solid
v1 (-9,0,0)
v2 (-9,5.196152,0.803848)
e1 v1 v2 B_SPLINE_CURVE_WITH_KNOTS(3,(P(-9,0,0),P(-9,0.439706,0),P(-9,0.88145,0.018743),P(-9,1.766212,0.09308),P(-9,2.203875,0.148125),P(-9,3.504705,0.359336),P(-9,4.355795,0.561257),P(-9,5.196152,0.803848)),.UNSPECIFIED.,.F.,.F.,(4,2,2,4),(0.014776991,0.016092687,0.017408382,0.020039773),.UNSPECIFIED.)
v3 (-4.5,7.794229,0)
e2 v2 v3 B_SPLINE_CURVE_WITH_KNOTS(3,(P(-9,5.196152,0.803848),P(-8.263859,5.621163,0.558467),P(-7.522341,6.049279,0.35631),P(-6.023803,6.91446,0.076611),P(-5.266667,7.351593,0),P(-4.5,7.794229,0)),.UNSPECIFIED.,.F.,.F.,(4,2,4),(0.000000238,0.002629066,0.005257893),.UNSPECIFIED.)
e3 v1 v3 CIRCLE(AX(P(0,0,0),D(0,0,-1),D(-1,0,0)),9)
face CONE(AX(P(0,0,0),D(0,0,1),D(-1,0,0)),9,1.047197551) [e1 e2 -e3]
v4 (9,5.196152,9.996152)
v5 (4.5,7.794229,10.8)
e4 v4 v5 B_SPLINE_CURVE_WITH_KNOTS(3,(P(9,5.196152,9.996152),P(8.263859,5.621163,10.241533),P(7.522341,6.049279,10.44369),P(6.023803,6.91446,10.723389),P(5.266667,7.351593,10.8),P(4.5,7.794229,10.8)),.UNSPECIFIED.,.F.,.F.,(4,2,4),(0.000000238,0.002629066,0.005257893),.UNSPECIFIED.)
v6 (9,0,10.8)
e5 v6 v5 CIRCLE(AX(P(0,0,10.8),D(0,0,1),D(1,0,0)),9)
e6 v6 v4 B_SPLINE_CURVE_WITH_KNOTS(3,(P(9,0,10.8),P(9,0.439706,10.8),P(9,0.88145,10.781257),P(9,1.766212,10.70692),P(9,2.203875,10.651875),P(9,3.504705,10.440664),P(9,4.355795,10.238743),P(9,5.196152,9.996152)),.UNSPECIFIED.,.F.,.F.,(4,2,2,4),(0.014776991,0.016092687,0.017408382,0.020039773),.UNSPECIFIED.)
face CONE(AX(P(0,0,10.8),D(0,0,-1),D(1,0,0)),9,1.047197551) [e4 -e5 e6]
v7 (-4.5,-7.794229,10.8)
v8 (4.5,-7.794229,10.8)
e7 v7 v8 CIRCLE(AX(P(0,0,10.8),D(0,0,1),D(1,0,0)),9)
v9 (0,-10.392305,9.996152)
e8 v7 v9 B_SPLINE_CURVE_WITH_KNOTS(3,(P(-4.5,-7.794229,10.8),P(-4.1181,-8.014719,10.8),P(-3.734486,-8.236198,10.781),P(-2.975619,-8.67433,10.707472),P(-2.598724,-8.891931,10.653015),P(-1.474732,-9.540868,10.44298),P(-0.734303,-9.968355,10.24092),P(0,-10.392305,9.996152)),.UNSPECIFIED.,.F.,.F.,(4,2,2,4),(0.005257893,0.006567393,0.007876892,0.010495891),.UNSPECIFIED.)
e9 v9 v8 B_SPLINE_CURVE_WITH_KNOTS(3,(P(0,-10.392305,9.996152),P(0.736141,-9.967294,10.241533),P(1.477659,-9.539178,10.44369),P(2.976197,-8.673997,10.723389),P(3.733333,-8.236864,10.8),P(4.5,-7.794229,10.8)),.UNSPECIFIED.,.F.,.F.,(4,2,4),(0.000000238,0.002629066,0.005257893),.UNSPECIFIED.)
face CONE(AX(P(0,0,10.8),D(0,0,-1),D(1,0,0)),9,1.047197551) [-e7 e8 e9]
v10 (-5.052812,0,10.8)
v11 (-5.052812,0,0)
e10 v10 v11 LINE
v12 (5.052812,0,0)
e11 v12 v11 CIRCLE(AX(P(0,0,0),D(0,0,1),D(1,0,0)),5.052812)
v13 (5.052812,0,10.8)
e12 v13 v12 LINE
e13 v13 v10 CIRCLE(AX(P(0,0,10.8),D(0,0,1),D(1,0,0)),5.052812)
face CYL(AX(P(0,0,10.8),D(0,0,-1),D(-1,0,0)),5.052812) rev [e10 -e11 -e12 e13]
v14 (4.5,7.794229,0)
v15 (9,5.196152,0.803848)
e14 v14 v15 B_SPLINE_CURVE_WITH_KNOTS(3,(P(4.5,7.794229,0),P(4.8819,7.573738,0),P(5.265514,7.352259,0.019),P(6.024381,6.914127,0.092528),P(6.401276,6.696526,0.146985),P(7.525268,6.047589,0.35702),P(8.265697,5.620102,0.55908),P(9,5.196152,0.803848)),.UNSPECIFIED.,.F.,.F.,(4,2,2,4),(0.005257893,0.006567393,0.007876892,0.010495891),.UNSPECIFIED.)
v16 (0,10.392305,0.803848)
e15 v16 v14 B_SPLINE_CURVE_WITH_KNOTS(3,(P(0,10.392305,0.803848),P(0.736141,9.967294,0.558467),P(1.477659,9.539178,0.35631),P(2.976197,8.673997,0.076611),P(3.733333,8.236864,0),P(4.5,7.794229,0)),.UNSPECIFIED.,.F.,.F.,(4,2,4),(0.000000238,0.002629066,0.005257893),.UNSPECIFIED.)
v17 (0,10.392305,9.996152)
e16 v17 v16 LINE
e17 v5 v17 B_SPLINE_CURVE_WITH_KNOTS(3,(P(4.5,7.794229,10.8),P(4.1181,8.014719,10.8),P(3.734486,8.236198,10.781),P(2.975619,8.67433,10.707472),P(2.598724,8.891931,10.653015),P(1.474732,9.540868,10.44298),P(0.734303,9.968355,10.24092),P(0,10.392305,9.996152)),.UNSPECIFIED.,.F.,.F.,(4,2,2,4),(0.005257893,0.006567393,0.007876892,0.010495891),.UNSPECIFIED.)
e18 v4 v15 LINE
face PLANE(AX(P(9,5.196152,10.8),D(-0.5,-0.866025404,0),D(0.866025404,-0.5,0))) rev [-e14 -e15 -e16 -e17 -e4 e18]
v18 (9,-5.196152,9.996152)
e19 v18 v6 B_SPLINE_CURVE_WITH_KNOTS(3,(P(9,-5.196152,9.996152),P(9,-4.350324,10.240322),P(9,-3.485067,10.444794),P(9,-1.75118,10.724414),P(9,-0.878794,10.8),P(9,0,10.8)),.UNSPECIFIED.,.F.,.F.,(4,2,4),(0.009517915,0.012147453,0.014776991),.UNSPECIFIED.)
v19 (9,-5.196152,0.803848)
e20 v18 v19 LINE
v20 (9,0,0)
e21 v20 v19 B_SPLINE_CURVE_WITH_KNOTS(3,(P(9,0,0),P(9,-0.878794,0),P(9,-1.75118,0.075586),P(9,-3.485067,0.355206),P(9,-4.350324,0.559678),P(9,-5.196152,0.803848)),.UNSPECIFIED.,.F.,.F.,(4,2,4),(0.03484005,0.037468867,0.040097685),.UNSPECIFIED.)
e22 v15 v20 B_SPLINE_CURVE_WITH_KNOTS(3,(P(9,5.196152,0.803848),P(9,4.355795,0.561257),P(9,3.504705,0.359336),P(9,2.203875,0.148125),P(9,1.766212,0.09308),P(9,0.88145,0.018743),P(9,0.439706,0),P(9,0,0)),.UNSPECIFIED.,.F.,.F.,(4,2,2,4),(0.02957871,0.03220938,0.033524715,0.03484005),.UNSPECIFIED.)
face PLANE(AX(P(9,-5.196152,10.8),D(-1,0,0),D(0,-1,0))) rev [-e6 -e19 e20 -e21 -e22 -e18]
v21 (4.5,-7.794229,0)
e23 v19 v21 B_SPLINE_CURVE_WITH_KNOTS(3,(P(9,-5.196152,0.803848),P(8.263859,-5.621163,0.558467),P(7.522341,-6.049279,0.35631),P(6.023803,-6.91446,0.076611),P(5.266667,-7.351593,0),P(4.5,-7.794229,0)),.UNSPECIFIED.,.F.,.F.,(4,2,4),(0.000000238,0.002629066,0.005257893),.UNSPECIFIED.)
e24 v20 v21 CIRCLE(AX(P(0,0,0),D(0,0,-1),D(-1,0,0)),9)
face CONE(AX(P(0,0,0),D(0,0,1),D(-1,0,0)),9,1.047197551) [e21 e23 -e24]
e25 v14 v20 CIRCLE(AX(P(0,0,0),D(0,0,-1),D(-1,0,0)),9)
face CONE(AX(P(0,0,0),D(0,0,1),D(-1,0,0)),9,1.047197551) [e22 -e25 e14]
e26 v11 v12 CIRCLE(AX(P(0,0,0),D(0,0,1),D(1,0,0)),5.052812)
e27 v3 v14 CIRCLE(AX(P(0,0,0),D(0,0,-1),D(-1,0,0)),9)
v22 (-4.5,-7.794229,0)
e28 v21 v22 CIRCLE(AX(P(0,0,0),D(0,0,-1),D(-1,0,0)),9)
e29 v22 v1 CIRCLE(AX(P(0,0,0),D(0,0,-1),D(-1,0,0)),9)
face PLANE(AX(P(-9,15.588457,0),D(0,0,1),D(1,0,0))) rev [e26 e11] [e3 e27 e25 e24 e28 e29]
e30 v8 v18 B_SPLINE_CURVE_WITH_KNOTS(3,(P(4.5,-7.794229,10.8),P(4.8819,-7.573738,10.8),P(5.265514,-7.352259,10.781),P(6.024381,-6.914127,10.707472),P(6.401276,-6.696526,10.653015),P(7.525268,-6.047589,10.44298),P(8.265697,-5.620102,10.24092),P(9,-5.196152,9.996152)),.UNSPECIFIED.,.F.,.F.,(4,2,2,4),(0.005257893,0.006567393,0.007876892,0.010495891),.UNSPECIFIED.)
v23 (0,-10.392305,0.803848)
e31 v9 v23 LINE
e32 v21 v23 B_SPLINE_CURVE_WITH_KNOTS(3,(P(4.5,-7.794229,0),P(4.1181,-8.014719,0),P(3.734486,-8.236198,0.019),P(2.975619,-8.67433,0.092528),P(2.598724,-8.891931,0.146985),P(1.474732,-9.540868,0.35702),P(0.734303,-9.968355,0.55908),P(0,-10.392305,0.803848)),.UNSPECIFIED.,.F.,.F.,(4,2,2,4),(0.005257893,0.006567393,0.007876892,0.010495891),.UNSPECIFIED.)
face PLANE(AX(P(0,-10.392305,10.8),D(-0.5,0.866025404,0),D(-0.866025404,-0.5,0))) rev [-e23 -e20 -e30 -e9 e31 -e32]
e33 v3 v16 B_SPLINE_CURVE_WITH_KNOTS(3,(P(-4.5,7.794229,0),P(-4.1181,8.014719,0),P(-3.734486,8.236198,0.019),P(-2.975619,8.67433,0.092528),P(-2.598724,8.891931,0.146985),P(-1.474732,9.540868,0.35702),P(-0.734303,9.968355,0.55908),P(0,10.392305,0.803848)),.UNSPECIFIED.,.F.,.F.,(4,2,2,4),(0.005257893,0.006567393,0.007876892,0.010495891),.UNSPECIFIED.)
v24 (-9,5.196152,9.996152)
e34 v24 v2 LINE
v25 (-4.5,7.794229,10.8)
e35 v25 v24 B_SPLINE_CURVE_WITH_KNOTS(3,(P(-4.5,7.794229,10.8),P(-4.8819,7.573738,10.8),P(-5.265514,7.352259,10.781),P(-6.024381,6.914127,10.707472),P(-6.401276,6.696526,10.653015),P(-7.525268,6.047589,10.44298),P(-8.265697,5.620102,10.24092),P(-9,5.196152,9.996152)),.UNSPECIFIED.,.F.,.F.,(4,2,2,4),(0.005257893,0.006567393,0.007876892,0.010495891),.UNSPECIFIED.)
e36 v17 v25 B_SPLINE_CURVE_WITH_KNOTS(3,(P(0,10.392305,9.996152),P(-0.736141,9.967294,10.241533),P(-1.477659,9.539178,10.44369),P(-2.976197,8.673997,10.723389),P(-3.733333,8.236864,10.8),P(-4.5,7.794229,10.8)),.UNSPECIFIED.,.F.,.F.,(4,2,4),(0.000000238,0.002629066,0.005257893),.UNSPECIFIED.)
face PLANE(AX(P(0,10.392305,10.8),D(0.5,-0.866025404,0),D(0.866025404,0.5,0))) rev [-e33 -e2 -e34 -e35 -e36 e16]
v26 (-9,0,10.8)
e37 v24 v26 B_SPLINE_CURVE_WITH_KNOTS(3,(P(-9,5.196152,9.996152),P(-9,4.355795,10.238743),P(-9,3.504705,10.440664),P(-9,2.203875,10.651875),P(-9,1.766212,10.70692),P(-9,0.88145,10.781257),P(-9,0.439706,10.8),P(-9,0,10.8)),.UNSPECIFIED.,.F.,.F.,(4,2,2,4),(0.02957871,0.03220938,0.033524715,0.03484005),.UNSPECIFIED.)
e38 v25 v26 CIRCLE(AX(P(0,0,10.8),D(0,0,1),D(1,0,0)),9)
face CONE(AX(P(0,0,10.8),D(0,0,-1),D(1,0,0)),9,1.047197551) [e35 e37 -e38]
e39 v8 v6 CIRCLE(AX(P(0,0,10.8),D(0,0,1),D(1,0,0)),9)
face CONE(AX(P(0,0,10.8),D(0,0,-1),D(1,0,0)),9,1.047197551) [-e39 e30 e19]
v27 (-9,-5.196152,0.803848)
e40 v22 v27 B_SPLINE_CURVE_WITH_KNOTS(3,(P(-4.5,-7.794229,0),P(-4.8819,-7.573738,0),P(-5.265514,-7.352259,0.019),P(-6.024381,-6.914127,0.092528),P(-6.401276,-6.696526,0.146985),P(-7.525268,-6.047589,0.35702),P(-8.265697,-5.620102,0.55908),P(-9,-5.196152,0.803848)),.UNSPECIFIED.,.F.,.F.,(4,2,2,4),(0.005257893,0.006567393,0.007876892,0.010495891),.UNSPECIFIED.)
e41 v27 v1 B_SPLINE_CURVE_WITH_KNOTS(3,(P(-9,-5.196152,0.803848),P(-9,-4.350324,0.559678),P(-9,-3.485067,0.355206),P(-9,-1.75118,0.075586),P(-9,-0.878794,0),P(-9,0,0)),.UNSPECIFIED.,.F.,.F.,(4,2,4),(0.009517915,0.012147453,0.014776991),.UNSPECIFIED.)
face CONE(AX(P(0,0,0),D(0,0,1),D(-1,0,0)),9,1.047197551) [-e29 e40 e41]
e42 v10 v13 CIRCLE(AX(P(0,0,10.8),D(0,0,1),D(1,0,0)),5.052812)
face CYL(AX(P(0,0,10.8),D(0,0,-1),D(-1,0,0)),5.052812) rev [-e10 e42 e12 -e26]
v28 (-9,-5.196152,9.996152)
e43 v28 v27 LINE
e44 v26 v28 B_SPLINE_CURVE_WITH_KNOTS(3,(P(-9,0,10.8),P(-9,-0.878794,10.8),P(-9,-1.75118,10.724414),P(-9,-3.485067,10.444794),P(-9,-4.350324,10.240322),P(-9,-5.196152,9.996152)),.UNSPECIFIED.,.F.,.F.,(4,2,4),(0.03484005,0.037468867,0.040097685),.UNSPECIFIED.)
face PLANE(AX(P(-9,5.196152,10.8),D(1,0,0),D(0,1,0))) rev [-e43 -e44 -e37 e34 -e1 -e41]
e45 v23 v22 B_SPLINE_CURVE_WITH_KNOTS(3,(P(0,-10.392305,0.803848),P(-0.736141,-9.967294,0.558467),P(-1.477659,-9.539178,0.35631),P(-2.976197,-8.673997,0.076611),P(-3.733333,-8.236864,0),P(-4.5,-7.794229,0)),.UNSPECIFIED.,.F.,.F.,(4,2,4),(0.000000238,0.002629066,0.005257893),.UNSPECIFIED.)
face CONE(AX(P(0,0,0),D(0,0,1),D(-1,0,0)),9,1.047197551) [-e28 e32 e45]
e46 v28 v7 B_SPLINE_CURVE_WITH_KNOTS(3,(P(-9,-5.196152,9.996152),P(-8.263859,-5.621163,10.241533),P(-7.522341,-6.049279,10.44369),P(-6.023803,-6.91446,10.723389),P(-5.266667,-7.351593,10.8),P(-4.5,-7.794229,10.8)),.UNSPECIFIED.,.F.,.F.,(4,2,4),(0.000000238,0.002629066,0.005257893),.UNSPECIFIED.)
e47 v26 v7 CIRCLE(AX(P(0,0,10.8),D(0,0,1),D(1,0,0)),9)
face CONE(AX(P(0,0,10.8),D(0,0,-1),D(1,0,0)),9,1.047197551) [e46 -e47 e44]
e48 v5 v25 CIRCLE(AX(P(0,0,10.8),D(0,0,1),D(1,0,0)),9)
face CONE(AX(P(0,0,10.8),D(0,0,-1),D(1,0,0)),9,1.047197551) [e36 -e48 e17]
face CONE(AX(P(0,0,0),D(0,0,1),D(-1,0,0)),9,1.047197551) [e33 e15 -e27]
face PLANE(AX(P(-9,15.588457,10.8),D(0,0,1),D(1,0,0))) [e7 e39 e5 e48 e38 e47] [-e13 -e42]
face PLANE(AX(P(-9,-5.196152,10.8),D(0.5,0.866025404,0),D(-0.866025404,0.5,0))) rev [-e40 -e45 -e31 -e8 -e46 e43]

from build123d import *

# Parameters (mm, degrees)
SKETCH_1_R          = 5.0528125
EXTRUDE_597_DEPTH   = 10.8
SKETCH_2_OUTSIDE_W  = 89.934
SKETCH_2_OUTSIDE_H  = 92.718
SKETCH_2_OUTSIDE_R  = 9
CUT_EXTRUDE_1_DEPTH = 18.482562741
CUT_EXTRUDE_1_DRAFT = -60
SKETCH_3_OUTSIDE_W  = 89.934
SKETCH_3_OUTSIDE_H  = 92.718
SKETCH_3_OUTSIDE_R  = 9
CUT_EXTRUDE_2_DEPTH = 18.482562741
CUT_EXTRUDE_2_DRAFT = -60


with BuildPart() as part:
    # 草图1 → Extrude 597 (new body)
    with BuildSketch(Plane.XY):
        Polygon((0, 10.392304845), (-9, 5.196152423), (-9, -5.196152423), (0, -10.392304845), (9, -5.196152423), (9, 5.196152423), align=None)
        with Locations(Location((0, 0, 0), (0, 0, 180))):
            Circle(SKETCH_1_R, mode=Mode.SUBTRACT)
    extrude(amount=EXTRUDE_597_DEPTH)


with BuildPart() as cut_extrude_1_tool:
    # 草图2 outside → 切除-拉伸1 (with draft: the straight prism first)
    with BuildSketch(Plane(origin=(0, 0, 0), x_dir=(-1, 0, 0), z_dir=(0, 0, -1))):
        Rectangle(SKETCH_2_OUTSIDE_W, SKETCH_2_OUTSIDE_H)
        Circle(SKETCH_2_OUTSIDE_R, mode=Mode.SUBTRACT)
    extrude(amount=-CUT_EXTRUDE_1_DEPTH)
    # 切除-拉伸1: the draft: its side faces are tilted about the plane it starts from
    cut_extrude_1_sides = [cut_extrude_1_tool.faces().sort_by_distance(p)[0] for p in [
        (0, -46.359, 9.241281371),
        (-44.967, 0, 9.241281371),
        (0, 46.359, 9.241281371),
        (44.967, 0, 9.241281371),
        (9, 0, 9.241281371),
    ]]
    draft(cut_extrude_1_sides, Plane(origin=(0, 0, 0), x_dir=(-1, 0, 0), z_dir=(0, 0, -1)), CUT_EXTRUDE_1_DRAFT)


with BuildPart() as part_1:
    add(part.part)

    # 切除-拉伸1: cut by cut_extrude_1_tool
    add(cut_extrude_1_tool.part, mode=Mode.SUBTRACT)


with BuildPart() as cut_extrude_2_tool:
    # 草图3 outside → 切除-拉伸2 (with draft: the straight prism first)
    with BuildSketch(Plane.XY.offset(10.8)):
        Rectangle(SKETCH_3_OUTSIDE_W, SKETCH_3_OUTSIDE_H)
        Circle(SKETCH_3_OUTSIDE_R, mode=Mode.SUBTRACT)
    extrude(amount=-CUT_EXTRUDE_2_DEPTH)
    # 切除-拉伸2: the draft: its side faces are tilted about the plane it starts from
    cut_extrude_2_sides = [cut_extrude_2_tool.faces().sort_by_distance(p)[0] for p in [
        (0, -46.359, 1.558718629),
        (44.967, 0, 1.558718629),
        (0, 46.359, 1.558718629),
        (-44.967, 0, 1.558718629),
        (-9, 0, 1.558718629),
    ]]
    draft(cut_extrude_2_sides, Plane.XY.offset(10.8), CUT_EXTRUDE_2_DRAFT)


with BuildPart() as part_2:
    add(part_1.part)

    # 切除-拉伸2: cut by cut_extrude_2_tool
    add(cut_extrude_2_tool.part, mode=Mode.SUBTRACT)


solid = part_2.part
